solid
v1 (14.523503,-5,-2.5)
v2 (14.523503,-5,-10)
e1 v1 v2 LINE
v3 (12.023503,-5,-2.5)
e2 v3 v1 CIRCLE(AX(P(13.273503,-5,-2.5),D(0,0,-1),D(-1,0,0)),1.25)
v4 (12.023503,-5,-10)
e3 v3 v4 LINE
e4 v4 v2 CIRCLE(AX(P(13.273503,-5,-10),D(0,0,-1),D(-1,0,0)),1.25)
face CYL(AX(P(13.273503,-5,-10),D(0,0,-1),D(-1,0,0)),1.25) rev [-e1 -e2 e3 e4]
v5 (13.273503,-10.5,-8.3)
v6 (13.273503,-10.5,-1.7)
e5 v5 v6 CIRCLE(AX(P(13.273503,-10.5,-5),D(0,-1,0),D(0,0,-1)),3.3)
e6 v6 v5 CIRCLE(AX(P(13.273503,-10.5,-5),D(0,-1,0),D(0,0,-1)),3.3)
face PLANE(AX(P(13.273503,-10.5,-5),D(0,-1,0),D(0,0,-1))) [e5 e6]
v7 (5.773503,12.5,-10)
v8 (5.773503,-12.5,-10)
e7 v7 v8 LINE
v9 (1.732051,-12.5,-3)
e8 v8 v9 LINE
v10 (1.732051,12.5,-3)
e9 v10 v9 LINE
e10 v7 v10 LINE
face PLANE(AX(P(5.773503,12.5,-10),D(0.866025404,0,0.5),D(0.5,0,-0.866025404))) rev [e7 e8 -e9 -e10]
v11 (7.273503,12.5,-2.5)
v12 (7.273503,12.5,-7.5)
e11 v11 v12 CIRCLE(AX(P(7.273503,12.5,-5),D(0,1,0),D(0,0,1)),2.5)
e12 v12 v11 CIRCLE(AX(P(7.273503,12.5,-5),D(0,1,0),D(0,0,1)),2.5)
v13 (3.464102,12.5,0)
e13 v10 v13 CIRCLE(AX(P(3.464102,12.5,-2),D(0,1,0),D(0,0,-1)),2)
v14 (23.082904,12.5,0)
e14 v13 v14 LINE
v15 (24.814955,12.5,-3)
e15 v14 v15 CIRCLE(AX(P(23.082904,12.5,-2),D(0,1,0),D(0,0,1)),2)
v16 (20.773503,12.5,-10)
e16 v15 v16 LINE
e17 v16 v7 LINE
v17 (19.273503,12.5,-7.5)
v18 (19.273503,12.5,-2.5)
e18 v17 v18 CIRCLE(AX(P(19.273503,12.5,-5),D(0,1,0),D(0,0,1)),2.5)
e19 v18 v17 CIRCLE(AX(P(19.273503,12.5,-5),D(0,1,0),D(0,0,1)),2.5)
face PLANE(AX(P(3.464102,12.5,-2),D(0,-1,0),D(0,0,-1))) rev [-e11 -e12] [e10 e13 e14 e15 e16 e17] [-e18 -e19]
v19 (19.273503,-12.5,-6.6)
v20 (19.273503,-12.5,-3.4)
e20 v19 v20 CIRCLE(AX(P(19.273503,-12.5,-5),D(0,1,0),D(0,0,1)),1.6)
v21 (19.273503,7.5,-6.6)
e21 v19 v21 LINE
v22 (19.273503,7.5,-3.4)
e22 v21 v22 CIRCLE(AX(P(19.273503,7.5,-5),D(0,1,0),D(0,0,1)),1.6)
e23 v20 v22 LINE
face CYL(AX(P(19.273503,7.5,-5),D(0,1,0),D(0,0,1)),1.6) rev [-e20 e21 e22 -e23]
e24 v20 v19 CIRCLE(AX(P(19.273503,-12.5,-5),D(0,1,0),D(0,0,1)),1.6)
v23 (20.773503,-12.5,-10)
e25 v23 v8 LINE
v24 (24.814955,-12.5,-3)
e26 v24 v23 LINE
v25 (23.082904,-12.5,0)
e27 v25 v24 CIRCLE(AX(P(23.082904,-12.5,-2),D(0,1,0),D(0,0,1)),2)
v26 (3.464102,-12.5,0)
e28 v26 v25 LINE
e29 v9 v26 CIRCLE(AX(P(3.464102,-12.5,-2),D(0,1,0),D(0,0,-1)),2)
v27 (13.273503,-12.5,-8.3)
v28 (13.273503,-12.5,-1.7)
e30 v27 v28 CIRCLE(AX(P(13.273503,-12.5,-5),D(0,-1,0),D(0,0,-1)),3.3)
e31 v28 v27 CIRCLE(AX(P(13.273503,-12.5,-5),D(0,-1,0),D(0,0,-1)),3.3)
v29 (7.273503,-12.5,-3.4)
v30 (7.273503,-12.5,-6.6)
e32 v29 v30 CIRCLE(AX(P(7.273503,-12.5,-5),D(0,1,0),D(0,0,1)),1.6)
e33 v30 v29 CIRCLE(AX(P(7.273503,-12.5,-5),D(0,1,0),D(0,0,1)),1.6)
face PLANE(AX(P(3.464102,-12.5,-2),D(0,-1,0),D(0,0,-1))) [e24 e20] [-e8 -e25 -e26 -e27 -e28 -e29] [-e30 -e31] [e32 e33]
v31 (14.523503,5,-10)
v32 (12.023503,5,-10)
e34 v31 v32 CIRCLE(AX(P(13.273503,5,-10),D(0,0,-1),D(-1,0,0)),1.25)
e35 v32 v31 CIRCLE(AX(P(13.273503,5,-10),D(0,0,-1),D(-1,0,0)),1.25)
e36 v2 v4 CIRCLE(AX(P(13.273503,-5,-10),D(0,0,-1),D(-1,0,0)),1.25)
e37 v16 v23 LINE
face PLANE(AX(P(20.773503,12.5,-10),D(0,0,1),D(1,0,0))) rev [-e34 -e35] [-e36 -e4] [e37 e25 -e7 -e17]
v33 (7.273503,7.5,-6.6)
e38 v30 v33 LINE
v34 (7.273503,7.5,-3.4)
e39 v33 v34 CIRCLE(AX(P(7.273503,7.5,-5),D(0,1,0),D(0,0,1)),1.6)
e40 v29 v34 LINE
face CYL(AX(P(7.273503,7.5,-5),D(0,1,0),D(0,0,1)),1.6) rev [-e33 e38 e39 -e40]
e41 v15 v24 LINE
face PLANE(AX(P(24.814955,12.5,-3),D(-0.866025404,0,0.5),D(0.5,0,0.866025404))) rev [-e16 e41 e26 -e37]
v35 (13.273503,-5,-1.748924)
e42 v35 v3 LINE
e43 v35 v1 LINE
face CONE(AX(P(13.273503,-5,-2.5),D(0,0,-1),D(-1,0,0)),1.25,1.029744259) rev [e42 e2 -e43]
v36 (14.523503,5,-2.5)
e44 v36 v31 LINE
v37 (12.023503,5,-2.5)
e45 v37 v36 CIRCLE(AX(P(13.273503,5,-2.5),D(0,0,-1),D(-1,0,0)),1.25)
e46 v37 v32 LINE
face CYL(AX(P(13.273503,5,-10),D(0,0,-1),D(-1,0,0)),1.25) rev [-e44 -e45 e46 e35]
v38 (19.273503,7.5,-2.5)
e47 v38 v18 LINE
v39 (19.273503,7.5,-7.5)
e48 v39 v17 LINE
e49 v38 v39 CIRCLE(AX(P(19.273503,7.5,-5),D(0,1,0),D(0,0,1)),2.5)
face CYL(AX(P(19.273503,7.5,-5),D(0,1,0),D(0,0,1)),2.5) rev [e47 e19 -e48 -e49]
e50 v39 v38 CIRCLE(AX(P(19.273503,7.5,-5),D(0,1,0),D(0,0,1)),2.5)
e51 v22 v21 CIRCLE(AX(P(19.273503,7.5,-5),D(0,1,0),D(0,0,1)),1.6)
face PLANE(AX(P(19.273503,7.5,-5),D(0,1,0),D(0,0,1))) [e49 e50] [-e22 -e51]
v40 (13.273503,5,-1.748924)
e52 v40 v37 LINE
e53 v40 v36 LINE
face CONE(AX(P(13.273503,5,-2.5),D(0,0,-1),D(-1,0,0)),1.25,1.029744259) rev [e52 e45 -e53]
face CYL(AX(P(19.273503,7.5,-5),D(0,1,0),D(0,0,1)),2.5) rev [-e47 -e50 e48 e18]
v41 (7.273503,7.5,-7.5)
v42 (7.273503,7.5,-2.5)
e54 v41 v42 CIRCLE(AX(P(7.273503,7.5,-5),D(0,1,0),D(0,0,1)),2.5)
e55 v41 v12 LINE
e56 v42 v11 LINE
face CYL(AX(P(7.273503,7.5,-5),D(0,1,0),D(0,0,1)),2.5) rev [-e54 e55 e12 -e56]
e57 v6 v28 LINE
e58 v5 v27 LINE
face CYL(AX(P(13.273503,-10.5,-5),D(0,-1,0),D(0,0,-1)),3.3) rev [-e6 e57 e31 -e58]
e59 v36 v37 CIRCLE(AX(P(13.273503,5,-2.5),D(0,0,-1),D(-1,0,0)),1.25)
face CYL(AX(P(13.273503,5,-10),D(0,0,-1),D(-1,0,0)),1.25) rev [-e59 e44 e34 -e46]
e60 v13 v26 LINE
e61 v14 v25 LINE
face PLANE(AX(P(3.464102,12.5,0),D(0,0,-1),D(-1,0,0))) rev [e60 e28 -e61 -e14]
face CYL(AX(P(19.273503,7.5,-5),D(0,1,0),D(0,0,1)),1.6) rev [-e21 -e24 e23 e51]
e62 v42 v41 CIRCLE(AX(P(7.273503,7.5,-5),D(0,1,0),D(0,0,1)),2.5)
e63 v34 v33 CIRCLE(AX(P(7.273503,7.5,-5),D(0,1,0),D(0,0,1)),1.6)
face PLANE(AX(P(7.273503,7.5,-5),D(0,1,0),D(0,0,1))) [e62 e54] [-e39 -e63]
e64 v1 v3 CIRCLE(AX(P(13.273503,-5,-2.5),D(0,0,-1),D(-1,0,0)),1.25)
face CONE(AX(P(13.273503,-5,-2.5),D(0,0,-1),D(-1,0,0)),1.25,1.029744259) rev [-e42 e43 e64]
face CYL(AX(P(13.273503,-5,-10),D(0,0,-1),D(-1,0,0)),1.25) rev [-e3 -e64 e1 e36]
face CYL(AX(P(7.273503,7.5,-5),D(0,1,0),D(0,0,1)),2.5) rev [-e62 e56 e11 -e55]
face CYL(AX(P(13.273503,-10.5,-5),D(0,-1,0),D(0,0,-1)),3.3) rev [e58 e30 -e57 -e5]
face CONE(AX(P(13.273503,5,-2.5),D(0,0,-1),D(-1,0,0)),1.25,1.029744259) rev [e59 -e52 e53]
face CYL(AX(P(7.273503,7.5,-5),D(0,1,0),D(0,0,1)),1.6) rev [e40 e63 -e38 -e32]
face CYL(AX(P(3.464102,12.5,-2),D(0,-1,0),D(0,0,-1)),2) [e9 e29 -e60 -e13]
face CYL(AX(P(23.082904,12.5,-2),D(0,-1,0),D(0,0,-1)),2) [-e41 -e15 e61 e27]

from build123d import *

# Parameters (mm, degrees)
BOSS_EXTRUDE1_DEPTH        = 12.5
SKETCH2_R                  = 2.5
CUT_EXTRUDE1_DEPTH         = 5
M3_TAPPED_HOLE1_D          = 2.5
M3_TAPPED_HOLE1_DEPTH      = 7.5
M3_TAPPED_HOLE1_TIP        = 0.751075774
F_3_2_3_2_DIAMETER_HOLE1_D = 3.2
SKETCH8_R                  = 3.3
CUT_EXTRUDE2_DEPTH         = 2


with BuildPart() as part:
    # Sketch1 → Boss-Extrude1 (new, symmetric)
    with BuildSketch(Plane(origin=(0, 0, 0), x_dir=(1, 0, 0), z_dir=(0, 1, 0))):
        with BuildLine():
            Line((3.464101615, 0), (23.082903769, 0))
            ThreePointArc((23.082903769, 0), (24.814954576, 1), (24.814954576, 3))
            Line((24.814954576, 3), (20.773502692, 10))
            Line((20.773502692, 10), (5.773502692, 10))
            Line((5.773502692, 10), (1.732050808, 3))
            ThreePointArc((1.732050808, 3), (1.732050808, 1), (3.464101615, 0))
        make_face()
    extrude(amount=BOSS_EXTRUDE1_DEPTH, both=True)

    # Sketch2 → Cut-Extrude1 (cut)
    with BuildSketch(Plane(origin=(0, 12.5, 0), x_dir=(1, 0, 0), z_dir=(0, 1, 0))):
        with Locations(Location((7.273502692, 5, 0), (0, 0, 270))):
            Circle(SKETCH2_R)
        with Locations(Location((19.273502692, 5, 0), (0, 0, 270))):
            Circle(SKETCH2_R)
    extrude(amount=-CUT_EXTRUDE1_DEPTH, mode=Mode.SUBTRACT)

    # M3 Tapped Hole1
    with Locations(Plane(origin=(0, 0, -10), x_dir=(-1, 0, 0), z_dir=(0, 0, -1))):
        with Locations((-13.273502692, -5), (-13.273502692, 5)):
            Hole(M3_TAPPED_HOLE1_D / 2, depth=M3_TAPPED_HOLE1_DEPTH)
            with Locations((0, 0, -(M3_TAPPED_HOLE1_DEPTH + M3_TAPPED_HOLE1_TIP / 2))):  # 118° drill point
                Cone(0, M3_TAPPED_HOLE1_D / 2, M3_TAPPED_HOLE1_TIP, mode=Mode.SUBTRACT)

    # Ø3.2 (3.2) Diameter Hole1 (through all)
    with Locations(Plane(origin=(0, 7.5, 0), x_dir=(-1, 0, 0), z_dir=(0, 1, 0))):
        with Locations((-19.273502692, -5), (-7.273502692, -5)):
            Hole(F_3_2_3_2_DIAMETER_HOLE1_D / 2)

    # Sketch8 → Cut-Extrude2 (cut)
    with BuildSketch(Plane.XZ.offset(12.5)):
        with Locations(Location((13.273502692, -5, 0), (0, 0, 270))):
            Circle(SKETCH8_R)
    extrude(amount=-CUT_EXTRUDE2_DEPTH, mode=Mode.SUBTRACT)


solid = part.part
